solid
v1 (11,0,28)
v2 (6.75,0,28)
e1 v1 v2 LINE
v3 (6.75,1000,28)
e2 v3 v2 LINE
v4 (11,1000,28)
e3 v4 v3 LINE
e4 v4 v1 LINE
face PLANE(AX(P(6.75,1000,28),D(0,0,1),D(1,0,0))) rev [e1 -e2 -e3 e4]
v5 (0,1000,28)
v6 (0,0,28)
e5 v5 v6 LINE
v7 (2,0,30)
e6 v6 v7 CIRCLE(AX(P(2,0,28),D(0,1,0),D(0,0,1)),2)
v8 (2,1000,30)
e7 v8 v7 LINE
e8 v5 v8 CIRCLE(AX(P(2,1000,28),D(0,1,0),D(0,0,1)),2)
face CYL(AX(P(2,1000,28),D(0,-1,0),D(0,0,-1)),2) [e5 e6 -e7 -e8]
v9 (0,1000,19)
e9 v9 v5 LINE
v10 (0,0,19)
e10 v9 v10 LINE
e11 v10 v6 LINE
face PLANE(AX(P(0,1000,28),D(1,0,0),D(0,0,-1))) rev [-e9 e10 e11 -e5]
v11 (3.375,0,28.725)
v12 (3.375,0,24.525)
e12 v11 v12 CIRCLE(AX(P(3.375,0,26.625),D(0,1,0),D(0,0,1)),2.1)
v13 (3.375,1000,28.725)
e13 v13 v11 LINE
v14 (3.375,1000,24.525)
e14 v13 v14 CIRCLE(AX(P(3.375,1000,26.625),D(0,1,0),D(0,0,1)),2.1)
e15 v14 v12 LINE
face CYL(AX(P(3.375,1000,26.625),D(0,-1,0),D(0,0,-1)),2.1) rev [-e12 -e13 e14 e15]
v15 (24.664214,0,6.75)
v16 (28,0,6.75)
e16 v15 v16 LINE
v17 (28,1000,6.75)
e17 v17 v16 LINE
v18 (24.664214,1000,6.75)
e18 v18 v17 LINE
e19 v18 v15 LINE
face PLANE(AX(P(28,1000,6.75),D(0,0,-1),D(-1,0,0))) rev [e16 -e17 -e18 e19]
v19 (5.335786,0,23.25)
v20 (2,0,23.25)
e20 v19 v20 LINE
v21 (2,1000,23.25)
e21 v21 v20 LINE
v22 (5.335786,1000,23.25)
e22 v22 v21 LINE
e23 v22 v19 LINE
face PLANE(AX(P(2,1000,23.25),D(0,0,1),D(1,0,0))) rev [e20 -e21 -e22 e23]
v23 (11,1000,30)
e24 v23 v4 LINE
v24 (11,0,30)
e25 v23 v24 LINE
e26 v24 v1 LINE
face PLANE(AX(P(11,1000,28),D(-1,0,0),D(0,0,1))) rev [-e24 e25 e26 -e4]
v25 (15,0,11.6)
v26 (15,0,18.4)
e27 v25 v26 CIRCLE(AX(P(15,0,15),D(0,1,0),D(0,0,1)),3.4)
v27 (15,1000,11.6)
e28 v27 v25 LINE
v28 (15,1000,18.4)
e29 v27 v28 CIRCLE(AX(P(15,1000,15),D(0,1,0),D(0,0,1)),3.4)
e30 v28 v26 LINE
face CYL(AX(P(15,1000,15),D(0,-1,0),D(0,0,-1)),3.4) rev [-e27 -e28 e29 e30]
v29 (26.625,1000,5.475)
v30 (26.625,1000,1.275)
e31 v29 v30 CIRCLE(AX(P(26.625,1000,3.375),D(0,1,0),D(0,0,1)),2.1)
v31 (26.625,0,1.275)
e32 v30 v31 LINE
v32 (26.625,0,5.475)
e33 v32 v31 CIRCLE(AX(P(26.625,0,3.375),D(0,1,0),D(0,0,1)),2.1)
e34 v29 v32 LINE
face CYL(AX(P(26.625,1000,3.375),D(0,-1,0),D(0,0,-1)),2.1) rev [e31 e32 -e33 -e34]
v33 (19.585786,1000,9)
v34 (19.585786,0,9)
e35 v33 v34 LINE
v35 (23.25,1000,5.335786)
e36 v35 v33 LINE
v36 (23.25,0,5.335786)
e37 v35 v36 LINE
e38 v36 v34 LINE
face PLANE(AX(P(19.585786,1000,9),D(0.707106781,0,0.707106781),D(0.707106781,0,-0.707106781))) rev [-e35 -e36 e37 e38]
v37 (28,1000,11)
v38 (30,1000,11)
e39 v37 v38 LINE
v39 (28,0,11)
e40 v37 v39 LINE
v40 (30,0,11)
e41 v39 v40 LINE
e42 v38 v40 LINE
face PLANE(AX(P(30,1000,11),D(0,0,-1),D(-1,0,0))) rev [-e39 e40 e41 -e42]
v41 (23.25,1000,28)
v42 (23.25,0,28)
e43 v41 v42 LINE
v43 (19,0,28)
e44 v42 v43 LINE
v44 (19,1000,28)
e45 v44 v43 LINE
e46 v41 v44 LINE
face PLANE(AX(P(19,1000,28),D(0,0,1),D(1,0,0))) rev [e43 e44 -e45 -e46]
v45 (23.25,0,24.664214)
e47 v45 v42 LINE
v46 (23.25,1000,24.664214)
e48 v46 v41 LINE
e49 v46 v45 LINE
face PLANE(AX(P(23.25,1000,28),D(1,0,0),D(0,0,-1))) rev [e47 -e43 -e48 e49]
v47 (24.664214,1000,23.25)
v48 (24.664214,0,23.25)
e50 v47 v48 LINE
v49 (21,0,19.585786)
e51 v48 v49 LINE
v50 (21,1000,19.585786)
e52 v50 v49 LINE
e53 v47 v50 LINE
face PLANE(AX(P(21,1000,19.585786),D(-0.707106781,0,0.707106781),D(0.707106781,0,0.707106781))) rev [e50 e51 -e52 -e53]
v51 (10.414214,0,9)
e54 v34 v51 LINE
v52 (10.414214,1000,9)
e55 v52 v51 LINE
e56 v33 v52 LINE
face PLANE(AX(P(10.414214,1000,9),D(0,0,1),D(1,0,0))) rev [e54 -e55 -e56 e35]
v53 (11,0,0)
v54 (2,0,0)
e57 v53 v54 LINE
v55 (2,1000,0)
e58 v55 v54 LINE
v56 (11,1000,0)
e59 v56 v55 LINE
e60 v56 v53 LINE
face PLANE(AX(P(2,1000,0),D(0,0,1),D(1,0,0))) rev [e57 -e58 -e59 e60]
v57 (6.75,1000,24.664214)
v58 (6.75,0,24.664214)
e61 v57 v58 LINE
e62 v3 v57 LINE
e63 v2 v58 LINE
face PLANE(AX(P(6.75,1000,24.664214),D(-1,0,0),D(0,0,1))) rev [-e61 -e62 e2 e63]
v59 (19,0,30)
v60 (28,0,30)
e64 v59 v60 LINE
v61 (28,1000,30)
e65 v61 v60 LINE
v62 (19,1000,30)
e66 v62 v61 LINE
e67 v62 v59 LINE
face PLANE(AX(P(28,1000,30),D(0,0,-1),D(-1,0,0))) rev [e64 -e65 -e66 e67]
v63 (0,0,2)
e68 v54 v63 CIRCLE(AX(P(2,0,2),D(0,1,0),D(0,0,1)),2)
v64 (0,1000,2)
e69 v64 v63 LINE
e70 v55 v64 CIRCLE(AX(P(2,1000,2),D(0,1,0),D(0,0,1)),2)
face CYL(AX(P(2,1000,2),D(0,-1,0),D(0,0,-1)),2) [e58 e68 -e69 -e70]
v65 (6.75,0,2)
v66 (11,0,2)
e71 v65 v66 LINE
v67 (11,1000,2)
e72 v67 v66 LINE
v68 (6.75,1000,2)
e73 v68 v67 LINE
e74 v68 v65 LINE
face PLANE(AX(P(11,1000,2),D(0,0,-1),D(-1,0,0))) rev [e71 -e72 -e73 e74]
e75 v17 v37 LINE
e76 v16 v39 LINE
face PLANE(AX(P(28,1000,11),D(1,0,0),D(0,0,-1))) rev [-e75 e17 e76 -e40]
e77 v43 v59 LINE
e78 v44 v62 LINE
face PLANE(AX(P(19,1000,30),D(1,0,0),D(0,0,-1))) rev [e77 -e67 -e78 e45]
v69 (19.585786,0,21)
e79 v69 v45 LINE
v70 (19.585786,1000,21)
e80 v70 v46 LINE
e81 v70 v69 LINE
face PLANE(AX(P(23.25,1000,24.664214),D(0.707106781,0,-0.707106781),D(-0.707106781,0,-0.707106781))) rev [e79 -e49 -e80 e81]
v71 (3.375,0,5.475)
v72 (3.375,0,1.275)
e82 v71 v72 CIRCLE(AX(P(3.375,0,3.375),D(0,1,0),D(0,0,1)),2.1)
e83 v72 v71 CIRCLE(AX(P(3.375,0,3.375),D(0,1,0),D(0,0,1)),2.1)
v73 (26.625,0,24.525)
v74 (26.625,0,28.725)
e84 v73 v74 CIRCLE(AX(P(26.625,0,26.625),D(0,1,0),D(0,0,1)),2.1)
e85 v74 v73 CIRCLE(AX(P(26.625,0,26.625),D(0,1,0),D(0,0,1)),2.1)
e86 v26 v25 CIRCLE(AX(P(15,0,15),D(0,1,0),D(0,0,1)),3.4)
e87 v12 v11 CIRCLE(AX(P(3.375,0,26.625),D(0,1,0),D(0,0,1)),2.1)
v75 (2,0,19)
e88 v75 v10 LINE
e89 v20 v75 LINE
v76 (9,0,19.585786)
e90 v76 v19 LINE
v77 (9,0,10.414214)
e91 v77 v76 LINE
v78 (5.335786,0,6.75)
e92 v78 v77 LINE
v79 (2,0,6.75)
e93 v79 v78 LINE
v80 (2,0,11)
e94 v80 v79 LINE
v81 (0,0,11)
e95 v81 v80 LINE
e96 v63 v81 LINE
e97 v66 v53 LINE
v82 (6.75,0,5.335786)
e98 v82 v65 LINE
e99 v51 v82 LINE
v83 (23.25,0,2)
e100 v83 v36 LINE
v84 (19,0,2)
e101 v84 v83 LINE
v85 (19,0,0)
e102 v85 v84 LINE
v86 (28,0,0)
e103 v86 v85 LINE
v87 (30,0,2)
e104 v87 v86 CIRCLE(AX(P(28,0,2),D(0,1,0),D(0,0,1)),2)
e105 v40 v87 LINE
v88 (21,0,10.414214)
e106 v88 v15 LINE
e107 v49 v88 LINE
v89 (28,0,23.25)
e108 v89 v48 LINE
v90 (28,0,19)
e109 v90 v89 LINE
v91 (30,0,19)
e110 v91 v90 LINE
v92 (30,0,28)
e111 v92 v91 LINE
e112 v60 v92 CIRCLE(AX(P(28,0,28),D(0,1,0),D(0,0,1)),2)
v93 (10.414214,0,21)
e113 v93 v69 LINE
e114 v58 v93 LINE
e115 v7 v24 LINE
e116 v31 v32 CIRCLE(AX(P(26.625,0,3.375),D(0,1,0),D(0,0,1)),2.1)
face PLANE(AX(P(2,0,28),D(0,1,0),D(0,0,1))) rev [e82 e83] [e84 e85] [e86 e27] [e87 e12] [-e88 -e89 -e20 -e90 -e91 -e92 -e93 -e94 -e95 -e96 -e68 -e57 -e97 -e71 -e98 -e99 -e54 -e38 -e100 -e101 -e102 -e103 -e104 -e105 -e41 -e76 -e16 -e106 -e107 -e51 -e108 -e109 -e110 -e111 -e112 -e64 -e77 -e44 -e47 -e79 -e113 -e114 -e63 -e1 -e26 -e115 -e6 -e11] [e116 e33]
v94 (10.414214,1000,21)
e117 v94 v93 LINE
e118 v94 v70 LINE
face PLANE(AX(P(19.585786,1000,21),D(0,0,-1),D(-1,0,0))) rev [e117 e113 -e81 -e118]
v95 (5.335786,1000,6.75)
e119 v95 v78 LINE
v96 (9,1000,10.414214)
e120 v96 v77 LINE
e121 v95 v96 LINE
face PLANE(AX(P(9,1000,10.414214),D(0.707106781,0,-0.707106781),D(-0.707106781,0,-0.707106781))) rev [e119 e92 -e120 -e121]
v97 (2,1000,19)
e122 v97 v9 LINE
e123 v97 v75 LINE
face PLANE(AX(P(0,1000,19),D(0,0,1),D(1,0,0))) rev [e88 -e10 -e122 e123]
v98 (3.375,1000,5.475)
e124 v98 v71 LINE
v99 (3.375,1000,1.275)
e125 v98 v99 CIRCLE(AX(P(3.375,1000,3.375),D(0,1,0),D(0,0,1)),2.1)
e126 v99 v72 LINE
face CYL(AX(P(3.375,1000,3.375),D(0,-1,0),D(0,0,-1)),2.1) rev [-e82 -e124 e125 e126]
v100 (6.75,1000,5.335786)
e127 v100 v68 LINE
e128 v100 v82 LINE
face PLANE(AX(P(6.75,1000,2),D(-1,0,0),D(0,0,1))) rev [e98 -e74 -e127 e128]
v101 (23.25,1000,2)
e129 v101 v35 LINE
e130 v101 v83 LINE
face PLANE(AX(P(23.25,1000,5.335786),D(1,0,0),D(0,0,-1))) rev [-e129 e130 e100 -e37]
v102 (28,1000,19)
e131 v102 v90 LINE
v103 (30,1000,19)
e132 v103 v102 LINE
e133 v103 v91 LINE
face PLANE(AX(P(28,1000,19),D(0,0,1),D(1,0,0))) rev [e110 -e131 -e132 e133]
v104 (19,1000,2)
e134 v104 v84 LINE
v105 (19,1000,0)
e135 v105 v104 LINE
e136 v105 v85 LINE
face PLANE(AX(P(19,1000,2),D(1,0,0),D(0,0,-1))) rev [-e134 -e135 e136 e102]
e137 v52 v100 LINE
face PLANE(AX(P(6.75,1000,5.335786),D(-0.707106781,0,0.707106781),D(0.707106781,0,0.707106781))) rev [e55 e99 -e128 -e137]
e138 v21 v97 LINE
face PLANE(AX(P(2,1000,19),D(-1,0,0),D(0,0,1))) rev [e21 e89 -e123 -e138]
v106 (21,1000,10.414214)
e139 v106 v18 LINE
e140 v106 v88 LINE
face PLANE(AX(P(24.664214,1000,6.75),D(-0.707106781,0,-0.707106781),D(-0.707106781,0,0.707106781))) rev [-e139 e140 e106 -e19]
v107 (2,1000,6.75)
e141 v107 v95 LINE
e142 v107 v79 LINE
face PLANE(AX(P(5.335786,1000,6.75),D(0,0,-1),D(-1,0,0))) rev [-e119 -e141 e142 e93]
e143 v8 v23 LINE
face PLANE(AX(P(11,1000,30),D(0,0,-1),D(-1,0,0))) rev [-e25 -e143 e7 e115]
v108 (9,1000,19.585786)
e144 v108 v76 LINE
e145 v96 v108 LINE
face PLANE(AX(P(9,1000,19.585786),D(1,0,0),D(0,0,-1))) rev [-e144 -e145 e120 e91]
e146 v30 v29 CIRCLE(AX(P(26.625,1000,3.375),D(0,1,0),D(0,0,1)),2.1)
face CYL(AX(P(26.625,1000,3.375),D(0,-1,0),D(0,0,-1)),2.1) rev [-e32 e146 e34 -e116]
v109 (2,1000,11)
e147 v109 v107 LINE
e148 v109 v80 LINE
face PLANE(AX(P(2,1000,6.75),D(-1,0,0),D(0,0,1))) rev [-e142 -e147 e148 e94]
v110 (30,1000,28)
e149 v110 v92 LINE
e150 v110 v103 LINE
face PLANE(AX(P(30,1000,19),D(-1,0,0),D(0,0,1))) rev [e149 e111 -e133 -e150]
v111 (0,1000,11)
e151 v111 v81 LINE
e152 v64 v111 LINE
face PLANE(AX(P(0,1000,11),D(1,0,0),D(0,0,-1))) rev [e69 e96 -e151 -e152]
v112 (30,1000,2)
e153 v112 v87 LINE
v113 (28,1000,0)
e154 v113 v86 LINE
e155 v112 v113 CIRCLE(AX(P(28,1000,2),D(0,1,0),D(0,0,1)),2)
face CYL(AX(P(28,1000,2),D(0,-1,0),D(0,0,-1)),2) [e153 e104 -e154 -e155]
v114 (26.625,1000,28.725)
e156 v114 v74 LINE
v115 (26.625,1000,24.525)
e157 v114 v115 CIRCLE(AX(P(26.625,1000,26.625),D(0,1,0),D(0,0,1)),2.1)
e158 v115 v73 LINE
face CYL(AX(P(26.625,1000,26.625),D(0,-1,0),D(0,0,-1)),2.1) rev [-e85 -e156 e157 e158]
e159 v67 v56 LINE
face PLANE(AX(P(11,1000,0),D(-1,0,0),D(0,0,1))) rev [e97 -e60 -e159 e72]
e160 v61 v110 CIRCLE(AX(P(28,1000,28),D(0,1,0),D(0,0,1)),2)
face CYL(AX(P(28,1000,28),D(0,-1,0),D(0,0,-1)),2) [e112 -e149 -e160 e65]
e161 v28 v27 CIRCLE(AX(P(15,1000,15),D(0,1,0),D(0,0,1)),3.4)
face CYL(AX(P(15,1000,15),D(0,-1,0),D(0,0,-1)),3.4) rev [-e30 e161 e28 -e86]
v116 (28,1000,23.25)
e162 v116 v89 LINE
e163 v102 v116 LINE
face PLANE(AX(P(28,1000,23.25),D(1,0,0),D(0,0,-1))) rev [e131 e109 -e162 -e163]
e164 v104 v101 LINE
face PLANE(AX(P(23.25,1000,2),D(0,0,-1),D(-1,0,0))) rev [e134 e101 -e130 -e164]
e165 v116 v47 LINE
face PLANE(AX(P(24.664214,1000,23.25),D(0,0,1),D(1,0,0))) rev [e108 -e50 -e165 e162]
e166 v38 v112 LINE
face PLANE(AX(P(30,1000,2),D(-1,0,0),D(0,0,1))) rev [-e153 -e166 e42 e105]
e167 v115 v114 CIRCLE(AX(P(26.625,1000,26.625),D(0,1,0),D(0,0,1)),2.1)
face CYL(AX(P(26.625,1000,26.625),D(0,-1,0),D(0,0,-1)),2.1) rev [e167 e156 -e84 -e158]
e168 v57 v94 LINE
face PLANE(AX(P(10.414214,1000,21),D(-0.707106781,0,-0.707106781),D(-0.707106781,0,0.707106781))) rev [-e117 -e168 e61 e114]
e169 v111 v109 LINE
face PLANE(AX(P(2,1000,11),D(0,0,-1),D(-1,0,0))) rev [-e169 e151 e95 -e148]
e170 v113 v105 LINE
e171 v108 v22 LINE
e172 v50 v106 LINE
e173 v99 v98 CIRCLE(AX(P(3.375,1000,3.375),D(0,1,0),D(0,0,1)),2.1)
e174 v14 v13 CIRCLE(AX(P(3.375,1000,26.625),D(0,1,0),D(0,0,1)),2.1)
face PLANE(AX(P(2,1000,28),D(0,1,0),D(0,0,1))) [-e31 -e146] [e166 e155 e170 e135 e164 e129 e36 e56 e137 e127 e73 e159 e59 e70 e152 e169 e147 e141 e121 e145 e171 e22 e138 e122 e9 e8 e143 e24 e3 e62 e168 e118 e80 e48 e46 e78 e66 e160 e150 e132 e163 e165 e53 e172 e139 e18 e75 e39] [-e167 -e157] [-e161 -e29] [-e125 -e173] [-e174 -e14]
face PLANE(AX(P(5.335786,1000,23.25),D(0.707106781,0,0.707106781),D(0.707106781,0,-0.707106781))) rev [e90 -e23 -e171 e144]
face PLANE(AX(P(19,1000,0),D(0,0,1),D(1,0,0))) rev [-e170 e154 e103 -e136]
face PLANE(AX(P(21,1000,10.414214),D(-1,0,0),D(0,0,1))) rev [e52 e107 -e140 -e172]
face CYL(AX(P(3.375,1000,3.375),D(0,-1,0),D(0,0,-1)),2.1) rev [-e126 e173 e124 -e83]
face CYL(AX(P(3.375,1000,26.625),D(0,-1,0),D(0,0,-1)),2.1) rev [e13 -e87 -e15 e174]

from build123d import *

# Parameters (mm, degrees)
SKETCH_1_R      = 2.1
SKETCH_1_R_2    = 3.4
EXTRUDE_1_DEPTH = 1000


with BuildPart() as part:
    # 草图1 → 拉伸1 (new body)
    with BuildSketch(Plane(origin=(0, 0, 0), x_dir=(1, 0, 0), z_dir=(0, 1, 0))):
        with BuildLine():
            Line((6.75, -28), (11, -28))
            Line((11, -28), (11, -30))
            Line((11, -30), (2, -30))
            ThreePointArc((2, -30), (0.585786438, -29.414213562), (0, -28))
            Line((0, -28), (0, -19))
            Line((0, -19), (2, -19))
            Line((2, -19), (2, -23.25))
            Line((2, -23.25), (5.335785999, -23.25))
            Line((5.335785999, -23.25), (9, -19.585785999))
            Line((9, -19.585785999), (9, -10.414214001))
            Line((9, -10.414214001), (5.335785999, -6.75))
            Line((5.335785999, -6.75), (2, -6.75))
            Line((2, -6.75), (2, -11))
            Line((2, -11), (0, -11))
            Line((0, -11), (0, -2))
            ThreePointArc((0, -2), (0.585786438, -0.585786438), (2, 0))
            Line((2, 0), (11, 0))
            Line((11, 0), (11, -2))
            Line((11, -2), (6.75, -2))
            Line((6.75, -2), (6.75, -5.335785999))
            Line((6.75, -5.335785999), (10.414214001, -9))
            Line((10.414214001, -9), (19.585785999, -9))
            Line((19.585785999, -9), (23.25, -5.335785999))
            Line((23.25, -5.335785999), (23.25, -2))
            Line((23.25, -2), (19, -2))
            Line((19, -2), (19, 0))
            Line((19, 0), (28, 0))
            ThreePointArc((28, 0), (29.414213562, -0.585786438), (30, -2))
            Line((30, -2), (30, -11))
            Line((30, -11), (28, -11))
            Line((28, -11), (28, -6.75))
            Line((28, -6.75), (24.664214001, -6.75))
            Line((24.664214001, -6.75), (21, -10.414214001))
            Line((21, -10.414214001), (21, -19.585785999))
            Line((21, -19.585785999), (24.664214001, -23.25))
            Line((24.664214001, -23.25), (28, -23.25))
            Line((28, -23.25), (28, -19))
            Line((28, -19), (30, -19))
            Line((30, -19), (30, -28))
            ThreePointArc((30, -28), (29.414213562, -29.414213562), (28, -30))
            Line((28, -30), (19, -30))
            Line((19, -30), (19, -28))
            Line((19, -28), (23.25, -28))
            Line((23.25, -28), (23.25, -24.664214001))
            Line((23.25, -24.664214001), (19.585785999, -21))
            Line((19.585785999, -21), (10.414214001, -21))
            Line((10.414214001, -21), (6.75, -24.664214001))
            Line((6.75, -24.664214001), (6.75, -28))
        make_face()
        with Locations(Location((3.375, -26.625, 0), (0, 0, 270))):
            Circle(SKETCH_1_R, mode=Mode.SUBTRACT)
        with Locations(Location((26.625, -26.625, 0), (0, 0, 270))):
            Circle(SKETCH_1_R, mode=Mode.SUBTRACT)
        with Locations(Location((15, -15, 0), (0, 0, 270))):
            Circle(SKETCH_1_R_2, mode=Mode.SUBTRACT)
        with Locations(Location((3.375, -3.375, 0), (0, 0, 270))):
            Circle(SKETCH_1_R, mode=Mode.SUBTRACT)
        with Locations(Location((26.625, -3.375, 0), (0, 0, 270))):
            Circle(SKETCH_1_R, mode=Mode.SUBTRACT)
    extrude(amount=EXTRUDE_1_DEPTH)


solid = part.part
